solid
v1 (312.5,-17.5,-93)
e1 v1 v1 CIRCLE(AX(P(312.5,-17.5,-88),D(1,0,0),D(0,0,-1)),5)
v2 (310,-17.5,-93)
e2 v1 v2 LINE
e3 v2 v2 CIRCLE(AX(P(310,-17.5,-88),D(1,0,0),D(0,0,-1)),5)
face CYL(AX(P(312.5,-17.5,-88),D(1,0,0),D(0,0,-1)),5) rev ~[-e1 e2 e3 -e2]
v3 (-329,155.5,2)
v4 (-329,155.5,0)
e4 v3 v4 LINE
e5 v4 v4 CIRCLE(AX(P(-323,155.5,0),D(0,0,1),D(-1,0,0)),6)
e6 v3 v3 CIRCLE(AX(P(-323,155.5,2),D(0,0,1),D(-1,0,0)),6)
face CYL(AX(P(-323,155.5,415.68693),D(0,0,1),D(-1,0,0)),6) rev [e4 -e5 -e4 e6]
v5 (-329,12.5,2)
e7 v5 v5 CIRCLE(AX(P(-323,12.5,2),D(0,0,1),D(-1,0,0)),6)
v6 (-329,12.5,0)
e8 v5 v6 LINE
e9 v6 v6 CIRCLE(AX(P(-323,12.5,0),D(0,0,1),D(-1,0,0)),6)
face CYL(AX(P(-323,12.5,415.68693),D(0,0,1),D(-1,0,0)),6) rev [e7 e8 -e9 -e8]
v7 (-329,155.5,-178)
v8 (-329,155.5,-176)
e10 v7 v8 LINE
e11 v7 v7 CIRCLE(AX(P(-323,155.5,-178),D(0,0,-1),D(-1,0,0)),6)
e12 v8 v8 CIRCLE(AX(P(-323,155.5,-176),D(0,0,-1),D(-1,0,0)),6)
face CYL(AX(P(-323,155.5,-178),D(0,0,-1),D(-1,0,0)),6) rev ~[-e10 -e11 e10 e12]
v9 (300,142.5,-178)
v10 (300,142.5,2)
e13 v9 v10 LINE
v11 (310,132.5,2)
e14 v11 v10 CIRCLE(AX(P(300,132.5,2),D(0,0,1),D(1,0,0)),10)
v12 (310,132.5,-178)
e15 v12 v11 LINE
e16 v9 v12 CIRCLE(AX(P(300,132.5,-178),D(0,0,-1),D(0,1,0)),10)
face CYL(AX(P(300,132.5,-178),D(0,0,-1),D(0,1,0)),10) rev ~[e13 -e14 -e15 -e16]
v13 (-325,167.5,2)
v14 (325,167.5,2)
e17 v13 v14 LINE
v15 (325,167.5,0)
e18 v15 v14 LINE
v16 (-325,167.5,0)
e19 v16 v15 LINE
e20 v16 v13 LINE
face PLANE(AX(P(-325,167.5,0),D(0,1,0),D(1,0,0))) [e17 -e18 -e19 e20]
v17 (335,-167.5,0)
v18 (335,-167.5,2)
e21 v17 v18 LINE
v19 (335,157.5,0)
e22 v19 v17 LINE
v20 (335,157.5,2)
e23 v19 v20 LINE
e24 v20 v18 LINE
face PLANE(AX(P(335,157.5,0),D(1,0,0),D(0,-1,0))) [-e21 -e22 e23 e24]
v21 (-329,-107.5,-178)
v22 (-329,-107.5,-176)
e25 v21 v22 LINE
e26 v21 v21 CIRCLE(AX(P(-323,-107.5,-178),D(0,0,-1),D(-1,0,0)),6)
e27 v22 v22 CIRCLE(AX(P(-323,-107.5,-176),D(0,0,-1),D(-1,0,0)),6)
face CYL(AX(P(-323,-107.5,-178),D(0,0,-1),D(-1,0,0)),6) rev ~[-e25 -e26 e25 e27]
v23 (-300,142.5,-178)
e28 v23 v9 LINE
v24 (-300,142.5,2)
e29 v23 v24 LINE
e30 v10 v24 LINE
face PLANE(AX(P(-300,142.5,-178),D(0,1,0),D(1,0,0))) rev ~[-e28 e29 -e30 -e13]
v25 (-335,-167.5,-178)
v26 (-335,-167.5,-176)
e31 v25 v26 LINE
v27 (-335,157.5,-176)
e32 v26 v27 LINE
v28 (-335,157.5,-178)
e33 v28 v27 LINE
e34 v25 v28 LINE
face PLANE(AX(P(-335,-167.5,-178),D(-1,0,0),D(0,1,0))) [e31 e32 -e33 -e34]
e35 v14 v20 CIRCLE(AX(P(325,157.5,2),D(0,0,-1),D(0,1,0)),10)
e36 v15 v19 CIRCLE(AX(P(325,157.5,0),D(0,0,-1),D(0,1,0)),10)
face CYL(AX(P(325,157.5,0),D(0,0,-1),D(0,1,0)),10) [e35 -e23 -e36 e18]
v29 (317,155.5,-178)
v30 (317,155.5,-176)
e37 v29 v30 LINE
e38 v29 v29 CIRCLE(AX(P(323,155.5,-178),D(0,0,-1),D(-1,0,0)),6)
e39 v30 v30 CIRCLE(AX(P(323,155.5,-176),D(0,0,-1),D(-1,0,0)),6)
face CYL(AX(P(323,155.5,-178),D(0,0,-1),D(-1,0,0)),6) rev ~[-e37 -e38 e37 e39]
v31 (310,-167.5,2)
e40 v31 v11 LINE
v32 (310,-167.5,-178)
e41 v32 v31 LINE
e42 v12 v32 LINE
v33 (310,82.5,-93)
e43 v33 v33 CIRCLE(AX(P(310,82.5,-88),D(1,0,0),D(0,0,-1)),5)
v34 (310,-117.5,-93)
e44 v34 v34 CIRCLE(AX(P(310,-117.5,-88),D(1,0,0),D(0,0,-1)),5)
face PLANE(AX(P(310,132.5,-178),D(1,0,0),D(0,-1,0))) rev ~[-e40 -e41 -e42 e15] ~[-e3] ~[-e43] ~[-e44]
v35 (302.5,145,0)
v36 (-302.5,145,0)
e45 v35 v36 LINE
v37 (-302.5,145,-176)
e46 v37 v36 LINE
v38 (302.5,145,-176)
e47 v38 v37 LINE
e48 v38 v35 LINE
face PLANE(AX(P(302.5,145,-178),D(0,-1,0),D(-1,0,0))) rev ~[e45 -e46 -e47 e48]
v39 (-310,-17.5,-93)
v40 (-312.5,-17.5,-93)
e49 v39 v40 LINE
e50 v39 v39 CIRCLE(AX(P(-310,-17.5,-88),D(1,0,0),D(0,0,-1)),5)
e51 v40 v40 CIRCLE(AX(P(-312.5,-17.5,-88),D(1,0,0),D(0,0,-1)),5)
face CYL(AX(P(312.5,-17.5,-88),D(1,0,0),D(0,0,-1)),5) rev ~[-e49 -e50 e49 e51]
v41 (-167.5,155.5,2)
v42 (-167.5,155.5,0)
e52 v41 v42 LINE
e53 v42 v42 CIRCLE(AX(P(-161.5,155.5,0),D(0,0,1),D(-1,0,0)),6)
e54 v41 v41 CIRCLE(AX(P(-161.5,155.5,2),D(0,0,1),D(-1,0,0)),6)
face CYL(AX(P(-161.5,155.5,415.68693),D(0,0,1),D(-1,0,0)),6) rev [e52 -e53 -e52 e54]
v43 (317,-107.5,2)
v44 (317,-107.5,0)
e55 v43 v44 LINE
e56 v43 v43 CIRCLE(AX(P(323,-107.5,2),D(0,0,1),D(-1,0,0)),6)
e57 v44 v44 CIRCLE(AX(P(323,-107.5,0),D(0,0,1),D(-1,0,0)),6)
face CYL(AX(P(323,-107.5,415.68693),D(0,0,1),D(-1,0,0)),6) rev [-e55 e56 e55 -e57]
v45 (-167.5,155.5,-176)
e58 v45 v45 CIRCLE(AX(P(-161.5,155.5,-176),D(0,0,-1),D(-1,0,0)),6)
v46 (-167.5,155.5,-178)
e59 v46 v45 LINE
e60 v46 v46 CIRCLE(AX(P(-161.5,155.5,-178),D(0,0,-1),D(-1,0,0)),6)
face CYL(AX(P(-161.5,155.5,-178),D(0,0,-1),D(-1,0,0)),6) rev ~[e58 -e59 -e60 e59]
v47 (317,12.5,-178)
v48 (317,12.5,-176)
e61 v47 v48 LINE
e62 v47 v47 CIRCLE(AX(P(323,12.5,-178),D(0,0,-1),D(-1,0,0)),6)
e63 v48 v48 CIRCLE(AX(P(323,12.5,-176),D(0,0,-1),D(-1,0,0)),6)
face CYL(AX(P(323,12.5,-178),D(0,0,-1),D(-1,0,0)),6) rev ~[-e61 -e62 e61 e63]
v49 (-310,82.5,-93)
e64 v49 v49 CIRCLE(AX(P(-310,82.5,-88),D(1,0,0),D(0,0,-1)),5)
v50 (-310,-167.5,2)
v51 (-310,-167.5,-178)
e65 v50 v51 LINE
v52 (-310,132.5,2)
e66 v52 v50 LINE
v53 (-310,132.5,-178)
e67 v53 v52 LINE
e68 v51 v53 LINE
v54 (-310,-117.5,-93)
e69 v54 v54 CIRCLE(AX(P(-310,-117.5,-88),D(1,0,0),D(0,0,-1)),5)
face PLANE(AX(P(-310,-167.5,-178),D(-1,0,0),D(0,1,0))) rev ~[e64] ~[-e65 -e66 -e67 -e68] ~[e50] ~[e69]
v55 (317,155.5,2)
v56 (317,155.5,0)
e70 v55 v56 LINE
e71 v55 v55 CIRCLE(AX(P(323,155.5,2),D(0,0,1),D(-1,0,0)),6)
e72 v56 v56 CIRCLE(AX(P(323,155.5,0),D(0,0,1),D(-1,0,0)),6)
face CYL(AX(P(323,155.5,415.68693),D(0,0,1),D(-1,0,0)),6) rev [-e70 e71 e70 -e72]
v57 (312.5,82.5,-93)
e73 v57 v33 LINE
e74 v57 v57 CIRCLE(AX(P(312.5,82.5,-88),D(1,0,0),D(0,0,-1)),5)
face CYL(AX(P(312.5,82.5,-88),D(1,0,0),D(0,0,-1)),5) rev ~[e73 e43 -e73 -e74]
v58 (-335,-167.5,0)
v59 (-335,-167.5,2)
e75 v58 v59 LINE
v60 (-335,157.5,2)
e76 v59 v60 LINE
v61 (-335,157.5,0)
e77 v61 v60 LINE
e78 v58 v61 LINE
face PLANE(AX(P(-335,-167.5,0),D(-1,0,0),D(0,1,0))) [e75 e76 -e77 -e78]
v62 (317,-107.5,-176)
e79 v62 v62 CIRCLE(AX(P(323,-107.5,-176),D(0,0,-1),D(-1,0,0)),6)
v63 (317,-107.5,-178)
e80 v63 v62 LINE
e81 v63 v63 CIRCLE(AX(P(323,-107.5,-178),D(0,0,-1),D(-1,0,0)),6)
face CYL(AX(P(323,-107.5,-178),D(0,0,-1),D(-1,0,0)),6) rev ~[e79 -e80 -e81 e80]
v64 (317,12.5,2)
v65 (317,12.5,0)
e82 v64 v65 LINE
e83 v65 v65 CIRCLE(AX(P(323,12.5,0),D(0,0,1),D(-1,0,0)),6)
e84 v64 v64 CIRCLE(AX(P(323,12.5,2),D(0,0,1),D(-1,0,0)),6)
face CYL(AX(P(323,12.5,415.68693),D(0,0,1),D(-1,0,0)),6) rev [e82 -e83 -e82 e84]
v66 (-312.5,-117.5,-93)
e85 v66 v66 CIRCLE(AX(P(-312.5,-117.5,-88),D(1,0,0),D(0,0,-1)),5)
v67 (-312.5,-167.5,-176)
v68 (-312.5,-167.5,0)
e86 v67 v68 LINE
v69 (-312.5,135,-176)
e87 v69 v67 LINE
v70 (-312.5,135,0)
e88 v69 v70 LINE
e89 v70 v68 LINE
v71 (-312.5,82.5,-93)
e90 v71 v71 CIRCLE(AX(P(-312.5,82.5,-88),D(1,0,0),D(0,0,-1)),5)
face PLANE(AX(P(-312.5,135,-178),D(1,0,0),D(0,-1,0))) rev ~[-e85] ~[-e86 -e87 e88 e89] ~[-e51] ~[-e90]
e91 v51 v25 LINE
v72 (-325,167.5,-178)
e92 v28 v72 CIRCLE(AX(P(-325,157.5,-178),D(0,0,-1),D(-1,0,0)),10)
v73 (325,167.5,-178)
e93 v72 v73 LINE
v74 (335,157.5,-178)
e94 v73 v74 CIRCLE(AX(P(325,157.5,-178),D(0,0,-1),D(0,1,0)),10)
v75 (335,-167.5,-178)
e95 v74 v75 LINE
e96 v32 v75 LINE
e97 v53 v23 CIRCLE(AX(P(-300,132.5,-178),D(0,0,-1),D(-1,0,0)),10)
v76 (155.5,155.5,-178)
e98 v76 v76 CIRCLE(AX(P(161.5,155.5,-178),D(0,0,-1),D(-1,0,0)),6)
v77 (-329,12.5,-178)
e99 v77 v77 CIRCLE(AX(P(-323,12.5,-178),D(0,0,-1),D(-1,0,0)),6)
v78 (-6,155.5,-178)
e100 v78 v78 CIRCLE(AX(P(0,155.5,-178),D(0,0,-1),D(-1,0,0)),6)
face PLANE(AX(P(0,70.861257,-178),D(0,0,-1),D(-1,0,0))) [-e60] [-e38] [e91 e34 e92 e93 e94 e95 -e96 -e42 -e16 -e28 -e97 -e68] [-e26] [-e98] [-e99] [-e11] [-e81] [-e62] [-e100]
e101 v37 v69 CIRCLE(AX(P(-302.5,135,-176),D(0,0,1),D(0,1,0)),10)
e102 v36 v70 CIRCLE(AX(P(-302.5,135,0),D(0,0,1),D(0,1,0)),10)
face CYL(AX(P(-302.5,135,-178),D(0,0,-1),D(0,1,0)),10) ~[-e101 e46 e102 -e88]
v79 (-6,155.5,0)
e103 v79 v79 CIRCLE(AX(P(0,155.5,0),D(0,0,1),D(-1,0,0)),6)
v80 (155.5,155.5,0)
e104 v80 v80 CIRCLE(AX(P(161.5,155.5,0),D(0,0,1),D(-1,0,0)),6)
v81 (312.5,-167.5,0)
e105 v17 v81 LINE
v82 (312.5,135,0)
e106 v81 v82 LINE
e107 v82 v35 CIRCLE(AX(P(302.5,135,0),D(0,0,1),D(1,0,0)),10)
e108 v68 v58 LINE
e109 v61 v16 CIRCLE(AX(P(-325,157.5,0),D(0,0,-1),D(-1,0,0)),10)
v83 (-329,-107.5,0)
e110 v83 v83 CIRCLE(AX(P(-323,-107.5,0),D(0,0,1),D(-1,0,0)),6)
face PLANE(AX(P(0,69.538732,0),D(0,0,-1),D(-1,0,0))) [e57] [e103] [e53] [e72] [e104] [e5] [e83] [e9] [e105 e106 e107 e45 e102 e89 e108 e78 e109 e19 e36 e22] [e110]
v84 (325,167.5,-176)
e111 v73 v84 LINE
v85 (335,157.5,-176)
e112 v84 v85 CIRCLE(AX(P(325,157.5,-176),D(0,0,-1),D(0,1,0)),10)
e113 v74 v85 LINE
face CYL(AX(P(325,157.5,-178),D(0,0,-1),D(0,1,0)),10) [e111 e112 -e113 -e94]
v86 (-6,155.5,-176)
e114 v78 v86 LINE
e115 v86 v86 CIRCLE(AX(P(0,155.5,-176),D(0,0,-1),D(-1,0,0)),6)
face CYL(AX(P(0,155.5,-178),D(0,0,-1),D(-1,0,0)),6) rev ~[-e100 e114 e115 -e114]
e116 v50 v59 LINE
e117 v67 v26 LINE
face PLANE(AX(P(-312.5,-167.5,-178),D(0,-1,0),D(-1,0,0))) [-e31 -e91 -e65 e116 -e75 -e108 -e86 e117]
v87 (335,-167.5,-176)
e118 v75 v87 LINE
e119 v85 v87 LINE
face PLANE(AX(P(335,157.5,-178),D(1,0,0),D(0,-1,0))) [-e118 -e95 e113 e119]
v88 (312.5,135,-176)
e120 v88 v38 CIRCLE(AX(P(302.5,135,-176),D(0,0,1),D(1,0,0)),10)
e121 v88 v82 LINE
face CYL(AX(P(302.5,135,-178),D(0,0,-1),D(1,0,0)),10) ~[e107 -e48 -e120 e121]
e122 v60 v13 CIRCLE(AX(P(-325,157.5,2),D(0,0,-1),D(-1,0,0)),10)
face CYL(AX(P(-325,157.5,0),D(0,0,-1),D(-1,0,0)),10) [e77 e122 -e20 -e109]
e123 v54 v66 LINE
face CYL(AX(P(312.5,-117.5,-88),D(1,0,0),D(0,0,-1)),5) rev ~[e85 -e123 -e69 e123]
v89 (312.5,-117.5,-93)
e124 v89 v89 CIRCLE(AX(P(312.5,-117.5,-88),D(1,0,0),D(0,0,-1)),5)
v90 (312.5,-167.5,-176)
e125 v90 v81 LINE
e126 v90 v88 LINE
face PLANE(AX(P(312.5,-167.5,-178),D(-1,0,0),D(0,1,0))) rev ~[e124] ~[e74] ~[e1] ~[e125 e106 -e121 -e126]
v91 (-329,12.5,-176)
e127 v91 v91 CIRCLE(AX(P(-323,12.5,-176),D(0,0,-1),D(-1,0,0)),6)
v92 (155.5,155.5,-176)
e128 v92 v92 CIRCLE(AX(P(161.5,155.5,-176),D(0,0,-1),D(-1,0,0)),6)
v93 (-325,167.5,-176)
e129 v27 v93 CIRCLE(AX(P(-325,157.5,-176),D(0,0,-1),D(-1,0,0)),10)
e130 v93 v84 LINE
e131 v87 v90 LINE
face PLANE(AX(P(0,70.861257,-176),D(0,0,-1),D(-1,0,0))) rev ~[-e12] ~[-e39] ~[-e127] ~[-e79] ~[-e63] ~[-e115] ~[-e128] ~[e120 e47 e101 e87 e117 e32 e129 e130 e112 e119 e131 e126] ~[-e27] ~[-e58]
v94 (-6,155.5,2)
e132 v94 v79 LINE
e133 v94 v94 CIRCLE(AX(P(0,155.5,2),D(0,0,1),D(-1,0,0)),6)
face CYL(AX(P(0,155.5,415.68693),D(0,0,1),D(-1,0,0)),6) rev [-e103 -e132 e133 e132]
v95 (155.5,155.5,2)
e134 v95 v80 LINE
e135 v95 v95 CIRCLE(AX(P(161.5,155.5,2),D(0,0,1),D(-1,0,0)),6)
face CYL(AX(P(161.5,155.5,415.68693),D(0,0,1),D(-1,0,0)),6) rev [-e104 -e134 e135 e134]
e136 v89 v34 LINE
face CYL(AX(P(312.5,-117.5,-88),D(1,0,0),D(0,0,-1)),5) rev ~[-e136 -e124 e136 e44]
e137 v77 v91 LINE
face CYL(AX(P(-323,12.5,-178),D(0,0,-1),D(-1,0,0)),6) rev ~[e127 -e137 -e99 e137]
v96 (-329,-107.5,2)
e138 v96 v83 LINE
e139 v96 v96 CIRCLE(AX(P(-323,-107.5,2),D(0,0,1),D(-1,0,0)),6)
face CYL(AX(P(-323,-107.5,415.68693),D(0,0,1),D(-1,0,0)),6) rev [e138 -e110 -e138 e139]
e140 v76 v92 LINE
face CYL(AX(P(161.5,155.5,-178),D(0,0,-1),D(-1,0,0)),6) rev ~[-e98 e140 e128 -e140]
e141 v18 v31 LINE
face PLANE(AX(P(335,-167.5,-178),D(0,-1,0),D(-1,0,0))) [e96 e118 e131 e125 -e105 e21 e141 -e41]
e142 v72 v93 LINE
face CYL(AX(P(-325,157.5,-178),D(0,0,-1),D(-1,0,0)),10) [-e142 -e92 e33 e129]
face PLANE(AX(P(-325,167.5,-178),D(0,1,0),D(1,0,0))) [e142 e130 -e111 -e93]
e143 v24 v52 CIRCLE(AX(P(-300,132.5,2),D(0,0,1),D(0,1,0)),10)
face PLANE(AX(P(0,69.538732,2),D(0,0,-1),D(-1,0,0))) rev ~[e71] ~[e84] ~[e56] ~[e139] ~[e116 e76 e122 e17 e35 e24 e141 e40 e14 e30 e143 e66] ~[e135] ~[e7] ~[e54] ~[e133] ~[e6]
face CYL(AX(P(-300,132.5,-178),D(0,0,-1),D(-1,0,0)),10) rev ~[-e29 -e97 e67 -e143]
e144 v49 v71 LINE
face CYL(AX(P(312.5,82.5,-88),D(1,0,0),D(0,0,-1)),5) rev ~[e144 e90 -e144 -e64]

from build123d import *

# Parameters (mm, degrees)
BOSS_EXTRUDE1_DEPTH     = 2
BOSS_EXTRUDE2_START     = 178
BOSS_EXTRUDE2_DEPTH     = 178
CUT_EXTRUDE1_DEPTH      = 415.686930105
CUT_EXTRUDE1_DEPTH_BACK = 415.686930105
SKETCH3_R               = 6
SKETCH4_R               = 5
CUT_EXTRUDE2_DEPTH      = 693.095730373
SKETCH5_R               = 6
BOSS_EXTRUDE3_DEPTH     = 2


with BuildPart() as part:
    # Sketch1 → Boss-Extrude1 (new body)
    with BuildSketch(Plane.XY):
        with BuildLine():
            Line((-335, -167.5), (-335, 157.5))
            ThreePointArc((-335, 157.5), (-332.071067812, 164.571067812), (-325, 167.5))
            Line((-325, 167.5), (325, 167.5))
            ThreePointArc((325, 167.5), (332.071067812, 164.571067812), (335, 157.5))
            Line((335, 157.5), (335, -167.5))
            Line((335, -167.5), (310, -167.5))
            Line((310, -167.5), (310, 132.5))
            ThreePointArc((310, 132.5), (307.071067812, 139.571067812), (300, 142.5))
            Line((300, 142.5), (-300, 142.5))
            ThreePointArc((-300, 142.5), (-307.071067812, 139.571067812), (-310, 132.5))
            Line((-310, 132.5), (-310, -167.5))
            Line((-310, -167.5), (-335, -167.5))
        make_face()
    extrude(amount=BOSS_EXTRUDE1_DEPTH)

    # Sketch2 → Boss-Extrude2 (add)
    with BuildSketch(Plane(origin=(0, 0, 0), x_dir=(-1, 0, 0), z_dir=(0, 0, -1)).offset(BOSS_EXTRUDE2_START)):
        with BuildLine():
            Line((310, -167.5), (310, 132.5))
            ThreePointArc((310, 132.5), (307.071067812, 139.571067812), (300, 142.5))
            Line((300, 142.5), (-300, 142.5))
            ThreePointArc((-300, 142.5), (-307.071067812, 139.571067812), (-310, 132.5))
            Line((-310, 132.5), (-310, -167.5))
            Line((-310, -167.5), (-312.5, -167.5))
            Line((-312.5, -167.5), (-312.5, 135))
            ThreePointArc((-312.5, 135), (-309.571067812, 142.071067812), (-302.5, 145))
            Line((-302.5, 145), (302.5, 145))
            ThreePointArc((302.5, 145), (309.571067812, 142.071067812), (312.5, 135))
            Line((312.5, 135), (312.5, -167.5))
            Line((312.5, -167.5), (310, -167.5))
        make_face()
    extrude(amount=-BOSS_EXTRUDE2_DEPTH)

    # Sketch3 → Cut-Extrude1 (cut, two sides: drawn at the far end of the back side and taken through both)
    with BuildSketch(Plane(origin=(0, 0, 0), x_dir=(-1, 0, 0), z_dir=(0, 0, -1)).offset(-CUT_EXTRUDE1_DEPTH_BACK)):
        with Locations((0, 155.5)):
            Circle(SKETCH3_R)
        with Locations((-161.5, 155.5)):
            Circle(SKETCH3_R)
        with Locations((-323, 12.5)):
            Circle(SKETCH3_R)
        with Locations((-323, -107.5)):
            Circle(SKETCH3_R)
        with Locations((-323, 155.5)):
            Circle(SKETCH3_R)
        with Locations((323, 155.5)):
            Circle(SKETCH3_R)
        with Locations((323, -107.5)):
            Circle(SKETCH3_R)
        with Locations((323, 12.5)):
            Circle(SKETCH3_R)
        with Locations((161.5, 155.5)):
            Circle(SKETCH3_R)
    extrude(amount=CUT_EXTRUDE1_DEPTH + CUT_EXTRUDE1_DEPTH_BACK, mode=Mode.SUBTRACT)

    # Sketch4 → Cut-Extrude2 (cut, through all)
    with BuildSketch(Plane(origin=(312.5, 0, 0), x_dir=(0, 0, -1), z_dir=(1, 0, 0))):
        with Locations((88, 82.5)):
            Circle(SKETCH4_R)
        with Locations((88, -17.5)):
            Circle(SKETCH4_R)
        with Locations((88, -117.5)):
            Circle(SKETCH4_R)
    extrude(amount=-CUT_EXTRUDE2_DEPTH, mode=Mode.SUBTRACT)

    # Sketch5 → Boss-Extrude3 (add)
    with BuildSketch(Plane(origin=(0, 0, -178), x_dir=(-1, 0, 0), z_dir=(0, 0, -1))):
        with BuildLine():
            Line((-312.5, -167.5), (-312.5, 135))
            ThreePointArc((-312.5, 135), (-309.571067812, 142.071067812), (-302.5, 145))
            Line((-302.5, 145), (302.5, 145))
            ThreePointArc((302.5, 145), (309.571067812, 142.071067812), (312.5, 135))
            Line((312.5, 135), (312.5, -167.5))
            Line((312.5, -167.5), (335, -167.5))
            Line((335, -167.5), (335, 157.5))
            ThreePointArc((335, 157.5), (332.071067812, 164.571067812), (325, 167.5))
            Line((325, 167.5), (-325, 167.5))
            ThreePointArc((-325, 167.5), (-332.071067812, 164.571067812), (-335, 157.5))
            Line((-335, 157.5), (-335, -167.5))
            Line((-335, -167.5), (-312.5, -167.5))
        make_face()
        with Locations((-323, -107.5)):
            Circle(SKETCH5_R, mode=Mode.SUBTRACT)
        with Locations((-323, 12.5)):
            Circle(SKETCH5_R, mode=Mode.SUBTRACT)
        with Locations((-161.5, 155.5)):
            Circle(SKETCH5_R, mode=Mode.SUBTRACT)
        with Locations((0, 155.5)):
            Circle(SKETCH5_R, mode=Mode.SUBTRACT)
        with Locations((161.5, 155.5)):
            Circle(SKETCH5_R, mode=Mode.SUBTRACT)
        with Locations((323, 12.5)):
            Circle(SKETCH5_R, mode=Mode.SUBTRACT)
        with Locations((323, -107.5)):
            Circle(SKETCH5_R, mode=Mode.SUBTRACT)
        with Locations((323, 155.5)):
            Circle(SKETCH5_R, mode=Mode.SUBTRACT)
        with Locations((-323, 155.5)):
            Circle(SKETCH5_R, mode=Mode.SUBTRACT)
    extrude(amount=-BOSS_EXTRUDE3_DEPTH)


solid = part.part
